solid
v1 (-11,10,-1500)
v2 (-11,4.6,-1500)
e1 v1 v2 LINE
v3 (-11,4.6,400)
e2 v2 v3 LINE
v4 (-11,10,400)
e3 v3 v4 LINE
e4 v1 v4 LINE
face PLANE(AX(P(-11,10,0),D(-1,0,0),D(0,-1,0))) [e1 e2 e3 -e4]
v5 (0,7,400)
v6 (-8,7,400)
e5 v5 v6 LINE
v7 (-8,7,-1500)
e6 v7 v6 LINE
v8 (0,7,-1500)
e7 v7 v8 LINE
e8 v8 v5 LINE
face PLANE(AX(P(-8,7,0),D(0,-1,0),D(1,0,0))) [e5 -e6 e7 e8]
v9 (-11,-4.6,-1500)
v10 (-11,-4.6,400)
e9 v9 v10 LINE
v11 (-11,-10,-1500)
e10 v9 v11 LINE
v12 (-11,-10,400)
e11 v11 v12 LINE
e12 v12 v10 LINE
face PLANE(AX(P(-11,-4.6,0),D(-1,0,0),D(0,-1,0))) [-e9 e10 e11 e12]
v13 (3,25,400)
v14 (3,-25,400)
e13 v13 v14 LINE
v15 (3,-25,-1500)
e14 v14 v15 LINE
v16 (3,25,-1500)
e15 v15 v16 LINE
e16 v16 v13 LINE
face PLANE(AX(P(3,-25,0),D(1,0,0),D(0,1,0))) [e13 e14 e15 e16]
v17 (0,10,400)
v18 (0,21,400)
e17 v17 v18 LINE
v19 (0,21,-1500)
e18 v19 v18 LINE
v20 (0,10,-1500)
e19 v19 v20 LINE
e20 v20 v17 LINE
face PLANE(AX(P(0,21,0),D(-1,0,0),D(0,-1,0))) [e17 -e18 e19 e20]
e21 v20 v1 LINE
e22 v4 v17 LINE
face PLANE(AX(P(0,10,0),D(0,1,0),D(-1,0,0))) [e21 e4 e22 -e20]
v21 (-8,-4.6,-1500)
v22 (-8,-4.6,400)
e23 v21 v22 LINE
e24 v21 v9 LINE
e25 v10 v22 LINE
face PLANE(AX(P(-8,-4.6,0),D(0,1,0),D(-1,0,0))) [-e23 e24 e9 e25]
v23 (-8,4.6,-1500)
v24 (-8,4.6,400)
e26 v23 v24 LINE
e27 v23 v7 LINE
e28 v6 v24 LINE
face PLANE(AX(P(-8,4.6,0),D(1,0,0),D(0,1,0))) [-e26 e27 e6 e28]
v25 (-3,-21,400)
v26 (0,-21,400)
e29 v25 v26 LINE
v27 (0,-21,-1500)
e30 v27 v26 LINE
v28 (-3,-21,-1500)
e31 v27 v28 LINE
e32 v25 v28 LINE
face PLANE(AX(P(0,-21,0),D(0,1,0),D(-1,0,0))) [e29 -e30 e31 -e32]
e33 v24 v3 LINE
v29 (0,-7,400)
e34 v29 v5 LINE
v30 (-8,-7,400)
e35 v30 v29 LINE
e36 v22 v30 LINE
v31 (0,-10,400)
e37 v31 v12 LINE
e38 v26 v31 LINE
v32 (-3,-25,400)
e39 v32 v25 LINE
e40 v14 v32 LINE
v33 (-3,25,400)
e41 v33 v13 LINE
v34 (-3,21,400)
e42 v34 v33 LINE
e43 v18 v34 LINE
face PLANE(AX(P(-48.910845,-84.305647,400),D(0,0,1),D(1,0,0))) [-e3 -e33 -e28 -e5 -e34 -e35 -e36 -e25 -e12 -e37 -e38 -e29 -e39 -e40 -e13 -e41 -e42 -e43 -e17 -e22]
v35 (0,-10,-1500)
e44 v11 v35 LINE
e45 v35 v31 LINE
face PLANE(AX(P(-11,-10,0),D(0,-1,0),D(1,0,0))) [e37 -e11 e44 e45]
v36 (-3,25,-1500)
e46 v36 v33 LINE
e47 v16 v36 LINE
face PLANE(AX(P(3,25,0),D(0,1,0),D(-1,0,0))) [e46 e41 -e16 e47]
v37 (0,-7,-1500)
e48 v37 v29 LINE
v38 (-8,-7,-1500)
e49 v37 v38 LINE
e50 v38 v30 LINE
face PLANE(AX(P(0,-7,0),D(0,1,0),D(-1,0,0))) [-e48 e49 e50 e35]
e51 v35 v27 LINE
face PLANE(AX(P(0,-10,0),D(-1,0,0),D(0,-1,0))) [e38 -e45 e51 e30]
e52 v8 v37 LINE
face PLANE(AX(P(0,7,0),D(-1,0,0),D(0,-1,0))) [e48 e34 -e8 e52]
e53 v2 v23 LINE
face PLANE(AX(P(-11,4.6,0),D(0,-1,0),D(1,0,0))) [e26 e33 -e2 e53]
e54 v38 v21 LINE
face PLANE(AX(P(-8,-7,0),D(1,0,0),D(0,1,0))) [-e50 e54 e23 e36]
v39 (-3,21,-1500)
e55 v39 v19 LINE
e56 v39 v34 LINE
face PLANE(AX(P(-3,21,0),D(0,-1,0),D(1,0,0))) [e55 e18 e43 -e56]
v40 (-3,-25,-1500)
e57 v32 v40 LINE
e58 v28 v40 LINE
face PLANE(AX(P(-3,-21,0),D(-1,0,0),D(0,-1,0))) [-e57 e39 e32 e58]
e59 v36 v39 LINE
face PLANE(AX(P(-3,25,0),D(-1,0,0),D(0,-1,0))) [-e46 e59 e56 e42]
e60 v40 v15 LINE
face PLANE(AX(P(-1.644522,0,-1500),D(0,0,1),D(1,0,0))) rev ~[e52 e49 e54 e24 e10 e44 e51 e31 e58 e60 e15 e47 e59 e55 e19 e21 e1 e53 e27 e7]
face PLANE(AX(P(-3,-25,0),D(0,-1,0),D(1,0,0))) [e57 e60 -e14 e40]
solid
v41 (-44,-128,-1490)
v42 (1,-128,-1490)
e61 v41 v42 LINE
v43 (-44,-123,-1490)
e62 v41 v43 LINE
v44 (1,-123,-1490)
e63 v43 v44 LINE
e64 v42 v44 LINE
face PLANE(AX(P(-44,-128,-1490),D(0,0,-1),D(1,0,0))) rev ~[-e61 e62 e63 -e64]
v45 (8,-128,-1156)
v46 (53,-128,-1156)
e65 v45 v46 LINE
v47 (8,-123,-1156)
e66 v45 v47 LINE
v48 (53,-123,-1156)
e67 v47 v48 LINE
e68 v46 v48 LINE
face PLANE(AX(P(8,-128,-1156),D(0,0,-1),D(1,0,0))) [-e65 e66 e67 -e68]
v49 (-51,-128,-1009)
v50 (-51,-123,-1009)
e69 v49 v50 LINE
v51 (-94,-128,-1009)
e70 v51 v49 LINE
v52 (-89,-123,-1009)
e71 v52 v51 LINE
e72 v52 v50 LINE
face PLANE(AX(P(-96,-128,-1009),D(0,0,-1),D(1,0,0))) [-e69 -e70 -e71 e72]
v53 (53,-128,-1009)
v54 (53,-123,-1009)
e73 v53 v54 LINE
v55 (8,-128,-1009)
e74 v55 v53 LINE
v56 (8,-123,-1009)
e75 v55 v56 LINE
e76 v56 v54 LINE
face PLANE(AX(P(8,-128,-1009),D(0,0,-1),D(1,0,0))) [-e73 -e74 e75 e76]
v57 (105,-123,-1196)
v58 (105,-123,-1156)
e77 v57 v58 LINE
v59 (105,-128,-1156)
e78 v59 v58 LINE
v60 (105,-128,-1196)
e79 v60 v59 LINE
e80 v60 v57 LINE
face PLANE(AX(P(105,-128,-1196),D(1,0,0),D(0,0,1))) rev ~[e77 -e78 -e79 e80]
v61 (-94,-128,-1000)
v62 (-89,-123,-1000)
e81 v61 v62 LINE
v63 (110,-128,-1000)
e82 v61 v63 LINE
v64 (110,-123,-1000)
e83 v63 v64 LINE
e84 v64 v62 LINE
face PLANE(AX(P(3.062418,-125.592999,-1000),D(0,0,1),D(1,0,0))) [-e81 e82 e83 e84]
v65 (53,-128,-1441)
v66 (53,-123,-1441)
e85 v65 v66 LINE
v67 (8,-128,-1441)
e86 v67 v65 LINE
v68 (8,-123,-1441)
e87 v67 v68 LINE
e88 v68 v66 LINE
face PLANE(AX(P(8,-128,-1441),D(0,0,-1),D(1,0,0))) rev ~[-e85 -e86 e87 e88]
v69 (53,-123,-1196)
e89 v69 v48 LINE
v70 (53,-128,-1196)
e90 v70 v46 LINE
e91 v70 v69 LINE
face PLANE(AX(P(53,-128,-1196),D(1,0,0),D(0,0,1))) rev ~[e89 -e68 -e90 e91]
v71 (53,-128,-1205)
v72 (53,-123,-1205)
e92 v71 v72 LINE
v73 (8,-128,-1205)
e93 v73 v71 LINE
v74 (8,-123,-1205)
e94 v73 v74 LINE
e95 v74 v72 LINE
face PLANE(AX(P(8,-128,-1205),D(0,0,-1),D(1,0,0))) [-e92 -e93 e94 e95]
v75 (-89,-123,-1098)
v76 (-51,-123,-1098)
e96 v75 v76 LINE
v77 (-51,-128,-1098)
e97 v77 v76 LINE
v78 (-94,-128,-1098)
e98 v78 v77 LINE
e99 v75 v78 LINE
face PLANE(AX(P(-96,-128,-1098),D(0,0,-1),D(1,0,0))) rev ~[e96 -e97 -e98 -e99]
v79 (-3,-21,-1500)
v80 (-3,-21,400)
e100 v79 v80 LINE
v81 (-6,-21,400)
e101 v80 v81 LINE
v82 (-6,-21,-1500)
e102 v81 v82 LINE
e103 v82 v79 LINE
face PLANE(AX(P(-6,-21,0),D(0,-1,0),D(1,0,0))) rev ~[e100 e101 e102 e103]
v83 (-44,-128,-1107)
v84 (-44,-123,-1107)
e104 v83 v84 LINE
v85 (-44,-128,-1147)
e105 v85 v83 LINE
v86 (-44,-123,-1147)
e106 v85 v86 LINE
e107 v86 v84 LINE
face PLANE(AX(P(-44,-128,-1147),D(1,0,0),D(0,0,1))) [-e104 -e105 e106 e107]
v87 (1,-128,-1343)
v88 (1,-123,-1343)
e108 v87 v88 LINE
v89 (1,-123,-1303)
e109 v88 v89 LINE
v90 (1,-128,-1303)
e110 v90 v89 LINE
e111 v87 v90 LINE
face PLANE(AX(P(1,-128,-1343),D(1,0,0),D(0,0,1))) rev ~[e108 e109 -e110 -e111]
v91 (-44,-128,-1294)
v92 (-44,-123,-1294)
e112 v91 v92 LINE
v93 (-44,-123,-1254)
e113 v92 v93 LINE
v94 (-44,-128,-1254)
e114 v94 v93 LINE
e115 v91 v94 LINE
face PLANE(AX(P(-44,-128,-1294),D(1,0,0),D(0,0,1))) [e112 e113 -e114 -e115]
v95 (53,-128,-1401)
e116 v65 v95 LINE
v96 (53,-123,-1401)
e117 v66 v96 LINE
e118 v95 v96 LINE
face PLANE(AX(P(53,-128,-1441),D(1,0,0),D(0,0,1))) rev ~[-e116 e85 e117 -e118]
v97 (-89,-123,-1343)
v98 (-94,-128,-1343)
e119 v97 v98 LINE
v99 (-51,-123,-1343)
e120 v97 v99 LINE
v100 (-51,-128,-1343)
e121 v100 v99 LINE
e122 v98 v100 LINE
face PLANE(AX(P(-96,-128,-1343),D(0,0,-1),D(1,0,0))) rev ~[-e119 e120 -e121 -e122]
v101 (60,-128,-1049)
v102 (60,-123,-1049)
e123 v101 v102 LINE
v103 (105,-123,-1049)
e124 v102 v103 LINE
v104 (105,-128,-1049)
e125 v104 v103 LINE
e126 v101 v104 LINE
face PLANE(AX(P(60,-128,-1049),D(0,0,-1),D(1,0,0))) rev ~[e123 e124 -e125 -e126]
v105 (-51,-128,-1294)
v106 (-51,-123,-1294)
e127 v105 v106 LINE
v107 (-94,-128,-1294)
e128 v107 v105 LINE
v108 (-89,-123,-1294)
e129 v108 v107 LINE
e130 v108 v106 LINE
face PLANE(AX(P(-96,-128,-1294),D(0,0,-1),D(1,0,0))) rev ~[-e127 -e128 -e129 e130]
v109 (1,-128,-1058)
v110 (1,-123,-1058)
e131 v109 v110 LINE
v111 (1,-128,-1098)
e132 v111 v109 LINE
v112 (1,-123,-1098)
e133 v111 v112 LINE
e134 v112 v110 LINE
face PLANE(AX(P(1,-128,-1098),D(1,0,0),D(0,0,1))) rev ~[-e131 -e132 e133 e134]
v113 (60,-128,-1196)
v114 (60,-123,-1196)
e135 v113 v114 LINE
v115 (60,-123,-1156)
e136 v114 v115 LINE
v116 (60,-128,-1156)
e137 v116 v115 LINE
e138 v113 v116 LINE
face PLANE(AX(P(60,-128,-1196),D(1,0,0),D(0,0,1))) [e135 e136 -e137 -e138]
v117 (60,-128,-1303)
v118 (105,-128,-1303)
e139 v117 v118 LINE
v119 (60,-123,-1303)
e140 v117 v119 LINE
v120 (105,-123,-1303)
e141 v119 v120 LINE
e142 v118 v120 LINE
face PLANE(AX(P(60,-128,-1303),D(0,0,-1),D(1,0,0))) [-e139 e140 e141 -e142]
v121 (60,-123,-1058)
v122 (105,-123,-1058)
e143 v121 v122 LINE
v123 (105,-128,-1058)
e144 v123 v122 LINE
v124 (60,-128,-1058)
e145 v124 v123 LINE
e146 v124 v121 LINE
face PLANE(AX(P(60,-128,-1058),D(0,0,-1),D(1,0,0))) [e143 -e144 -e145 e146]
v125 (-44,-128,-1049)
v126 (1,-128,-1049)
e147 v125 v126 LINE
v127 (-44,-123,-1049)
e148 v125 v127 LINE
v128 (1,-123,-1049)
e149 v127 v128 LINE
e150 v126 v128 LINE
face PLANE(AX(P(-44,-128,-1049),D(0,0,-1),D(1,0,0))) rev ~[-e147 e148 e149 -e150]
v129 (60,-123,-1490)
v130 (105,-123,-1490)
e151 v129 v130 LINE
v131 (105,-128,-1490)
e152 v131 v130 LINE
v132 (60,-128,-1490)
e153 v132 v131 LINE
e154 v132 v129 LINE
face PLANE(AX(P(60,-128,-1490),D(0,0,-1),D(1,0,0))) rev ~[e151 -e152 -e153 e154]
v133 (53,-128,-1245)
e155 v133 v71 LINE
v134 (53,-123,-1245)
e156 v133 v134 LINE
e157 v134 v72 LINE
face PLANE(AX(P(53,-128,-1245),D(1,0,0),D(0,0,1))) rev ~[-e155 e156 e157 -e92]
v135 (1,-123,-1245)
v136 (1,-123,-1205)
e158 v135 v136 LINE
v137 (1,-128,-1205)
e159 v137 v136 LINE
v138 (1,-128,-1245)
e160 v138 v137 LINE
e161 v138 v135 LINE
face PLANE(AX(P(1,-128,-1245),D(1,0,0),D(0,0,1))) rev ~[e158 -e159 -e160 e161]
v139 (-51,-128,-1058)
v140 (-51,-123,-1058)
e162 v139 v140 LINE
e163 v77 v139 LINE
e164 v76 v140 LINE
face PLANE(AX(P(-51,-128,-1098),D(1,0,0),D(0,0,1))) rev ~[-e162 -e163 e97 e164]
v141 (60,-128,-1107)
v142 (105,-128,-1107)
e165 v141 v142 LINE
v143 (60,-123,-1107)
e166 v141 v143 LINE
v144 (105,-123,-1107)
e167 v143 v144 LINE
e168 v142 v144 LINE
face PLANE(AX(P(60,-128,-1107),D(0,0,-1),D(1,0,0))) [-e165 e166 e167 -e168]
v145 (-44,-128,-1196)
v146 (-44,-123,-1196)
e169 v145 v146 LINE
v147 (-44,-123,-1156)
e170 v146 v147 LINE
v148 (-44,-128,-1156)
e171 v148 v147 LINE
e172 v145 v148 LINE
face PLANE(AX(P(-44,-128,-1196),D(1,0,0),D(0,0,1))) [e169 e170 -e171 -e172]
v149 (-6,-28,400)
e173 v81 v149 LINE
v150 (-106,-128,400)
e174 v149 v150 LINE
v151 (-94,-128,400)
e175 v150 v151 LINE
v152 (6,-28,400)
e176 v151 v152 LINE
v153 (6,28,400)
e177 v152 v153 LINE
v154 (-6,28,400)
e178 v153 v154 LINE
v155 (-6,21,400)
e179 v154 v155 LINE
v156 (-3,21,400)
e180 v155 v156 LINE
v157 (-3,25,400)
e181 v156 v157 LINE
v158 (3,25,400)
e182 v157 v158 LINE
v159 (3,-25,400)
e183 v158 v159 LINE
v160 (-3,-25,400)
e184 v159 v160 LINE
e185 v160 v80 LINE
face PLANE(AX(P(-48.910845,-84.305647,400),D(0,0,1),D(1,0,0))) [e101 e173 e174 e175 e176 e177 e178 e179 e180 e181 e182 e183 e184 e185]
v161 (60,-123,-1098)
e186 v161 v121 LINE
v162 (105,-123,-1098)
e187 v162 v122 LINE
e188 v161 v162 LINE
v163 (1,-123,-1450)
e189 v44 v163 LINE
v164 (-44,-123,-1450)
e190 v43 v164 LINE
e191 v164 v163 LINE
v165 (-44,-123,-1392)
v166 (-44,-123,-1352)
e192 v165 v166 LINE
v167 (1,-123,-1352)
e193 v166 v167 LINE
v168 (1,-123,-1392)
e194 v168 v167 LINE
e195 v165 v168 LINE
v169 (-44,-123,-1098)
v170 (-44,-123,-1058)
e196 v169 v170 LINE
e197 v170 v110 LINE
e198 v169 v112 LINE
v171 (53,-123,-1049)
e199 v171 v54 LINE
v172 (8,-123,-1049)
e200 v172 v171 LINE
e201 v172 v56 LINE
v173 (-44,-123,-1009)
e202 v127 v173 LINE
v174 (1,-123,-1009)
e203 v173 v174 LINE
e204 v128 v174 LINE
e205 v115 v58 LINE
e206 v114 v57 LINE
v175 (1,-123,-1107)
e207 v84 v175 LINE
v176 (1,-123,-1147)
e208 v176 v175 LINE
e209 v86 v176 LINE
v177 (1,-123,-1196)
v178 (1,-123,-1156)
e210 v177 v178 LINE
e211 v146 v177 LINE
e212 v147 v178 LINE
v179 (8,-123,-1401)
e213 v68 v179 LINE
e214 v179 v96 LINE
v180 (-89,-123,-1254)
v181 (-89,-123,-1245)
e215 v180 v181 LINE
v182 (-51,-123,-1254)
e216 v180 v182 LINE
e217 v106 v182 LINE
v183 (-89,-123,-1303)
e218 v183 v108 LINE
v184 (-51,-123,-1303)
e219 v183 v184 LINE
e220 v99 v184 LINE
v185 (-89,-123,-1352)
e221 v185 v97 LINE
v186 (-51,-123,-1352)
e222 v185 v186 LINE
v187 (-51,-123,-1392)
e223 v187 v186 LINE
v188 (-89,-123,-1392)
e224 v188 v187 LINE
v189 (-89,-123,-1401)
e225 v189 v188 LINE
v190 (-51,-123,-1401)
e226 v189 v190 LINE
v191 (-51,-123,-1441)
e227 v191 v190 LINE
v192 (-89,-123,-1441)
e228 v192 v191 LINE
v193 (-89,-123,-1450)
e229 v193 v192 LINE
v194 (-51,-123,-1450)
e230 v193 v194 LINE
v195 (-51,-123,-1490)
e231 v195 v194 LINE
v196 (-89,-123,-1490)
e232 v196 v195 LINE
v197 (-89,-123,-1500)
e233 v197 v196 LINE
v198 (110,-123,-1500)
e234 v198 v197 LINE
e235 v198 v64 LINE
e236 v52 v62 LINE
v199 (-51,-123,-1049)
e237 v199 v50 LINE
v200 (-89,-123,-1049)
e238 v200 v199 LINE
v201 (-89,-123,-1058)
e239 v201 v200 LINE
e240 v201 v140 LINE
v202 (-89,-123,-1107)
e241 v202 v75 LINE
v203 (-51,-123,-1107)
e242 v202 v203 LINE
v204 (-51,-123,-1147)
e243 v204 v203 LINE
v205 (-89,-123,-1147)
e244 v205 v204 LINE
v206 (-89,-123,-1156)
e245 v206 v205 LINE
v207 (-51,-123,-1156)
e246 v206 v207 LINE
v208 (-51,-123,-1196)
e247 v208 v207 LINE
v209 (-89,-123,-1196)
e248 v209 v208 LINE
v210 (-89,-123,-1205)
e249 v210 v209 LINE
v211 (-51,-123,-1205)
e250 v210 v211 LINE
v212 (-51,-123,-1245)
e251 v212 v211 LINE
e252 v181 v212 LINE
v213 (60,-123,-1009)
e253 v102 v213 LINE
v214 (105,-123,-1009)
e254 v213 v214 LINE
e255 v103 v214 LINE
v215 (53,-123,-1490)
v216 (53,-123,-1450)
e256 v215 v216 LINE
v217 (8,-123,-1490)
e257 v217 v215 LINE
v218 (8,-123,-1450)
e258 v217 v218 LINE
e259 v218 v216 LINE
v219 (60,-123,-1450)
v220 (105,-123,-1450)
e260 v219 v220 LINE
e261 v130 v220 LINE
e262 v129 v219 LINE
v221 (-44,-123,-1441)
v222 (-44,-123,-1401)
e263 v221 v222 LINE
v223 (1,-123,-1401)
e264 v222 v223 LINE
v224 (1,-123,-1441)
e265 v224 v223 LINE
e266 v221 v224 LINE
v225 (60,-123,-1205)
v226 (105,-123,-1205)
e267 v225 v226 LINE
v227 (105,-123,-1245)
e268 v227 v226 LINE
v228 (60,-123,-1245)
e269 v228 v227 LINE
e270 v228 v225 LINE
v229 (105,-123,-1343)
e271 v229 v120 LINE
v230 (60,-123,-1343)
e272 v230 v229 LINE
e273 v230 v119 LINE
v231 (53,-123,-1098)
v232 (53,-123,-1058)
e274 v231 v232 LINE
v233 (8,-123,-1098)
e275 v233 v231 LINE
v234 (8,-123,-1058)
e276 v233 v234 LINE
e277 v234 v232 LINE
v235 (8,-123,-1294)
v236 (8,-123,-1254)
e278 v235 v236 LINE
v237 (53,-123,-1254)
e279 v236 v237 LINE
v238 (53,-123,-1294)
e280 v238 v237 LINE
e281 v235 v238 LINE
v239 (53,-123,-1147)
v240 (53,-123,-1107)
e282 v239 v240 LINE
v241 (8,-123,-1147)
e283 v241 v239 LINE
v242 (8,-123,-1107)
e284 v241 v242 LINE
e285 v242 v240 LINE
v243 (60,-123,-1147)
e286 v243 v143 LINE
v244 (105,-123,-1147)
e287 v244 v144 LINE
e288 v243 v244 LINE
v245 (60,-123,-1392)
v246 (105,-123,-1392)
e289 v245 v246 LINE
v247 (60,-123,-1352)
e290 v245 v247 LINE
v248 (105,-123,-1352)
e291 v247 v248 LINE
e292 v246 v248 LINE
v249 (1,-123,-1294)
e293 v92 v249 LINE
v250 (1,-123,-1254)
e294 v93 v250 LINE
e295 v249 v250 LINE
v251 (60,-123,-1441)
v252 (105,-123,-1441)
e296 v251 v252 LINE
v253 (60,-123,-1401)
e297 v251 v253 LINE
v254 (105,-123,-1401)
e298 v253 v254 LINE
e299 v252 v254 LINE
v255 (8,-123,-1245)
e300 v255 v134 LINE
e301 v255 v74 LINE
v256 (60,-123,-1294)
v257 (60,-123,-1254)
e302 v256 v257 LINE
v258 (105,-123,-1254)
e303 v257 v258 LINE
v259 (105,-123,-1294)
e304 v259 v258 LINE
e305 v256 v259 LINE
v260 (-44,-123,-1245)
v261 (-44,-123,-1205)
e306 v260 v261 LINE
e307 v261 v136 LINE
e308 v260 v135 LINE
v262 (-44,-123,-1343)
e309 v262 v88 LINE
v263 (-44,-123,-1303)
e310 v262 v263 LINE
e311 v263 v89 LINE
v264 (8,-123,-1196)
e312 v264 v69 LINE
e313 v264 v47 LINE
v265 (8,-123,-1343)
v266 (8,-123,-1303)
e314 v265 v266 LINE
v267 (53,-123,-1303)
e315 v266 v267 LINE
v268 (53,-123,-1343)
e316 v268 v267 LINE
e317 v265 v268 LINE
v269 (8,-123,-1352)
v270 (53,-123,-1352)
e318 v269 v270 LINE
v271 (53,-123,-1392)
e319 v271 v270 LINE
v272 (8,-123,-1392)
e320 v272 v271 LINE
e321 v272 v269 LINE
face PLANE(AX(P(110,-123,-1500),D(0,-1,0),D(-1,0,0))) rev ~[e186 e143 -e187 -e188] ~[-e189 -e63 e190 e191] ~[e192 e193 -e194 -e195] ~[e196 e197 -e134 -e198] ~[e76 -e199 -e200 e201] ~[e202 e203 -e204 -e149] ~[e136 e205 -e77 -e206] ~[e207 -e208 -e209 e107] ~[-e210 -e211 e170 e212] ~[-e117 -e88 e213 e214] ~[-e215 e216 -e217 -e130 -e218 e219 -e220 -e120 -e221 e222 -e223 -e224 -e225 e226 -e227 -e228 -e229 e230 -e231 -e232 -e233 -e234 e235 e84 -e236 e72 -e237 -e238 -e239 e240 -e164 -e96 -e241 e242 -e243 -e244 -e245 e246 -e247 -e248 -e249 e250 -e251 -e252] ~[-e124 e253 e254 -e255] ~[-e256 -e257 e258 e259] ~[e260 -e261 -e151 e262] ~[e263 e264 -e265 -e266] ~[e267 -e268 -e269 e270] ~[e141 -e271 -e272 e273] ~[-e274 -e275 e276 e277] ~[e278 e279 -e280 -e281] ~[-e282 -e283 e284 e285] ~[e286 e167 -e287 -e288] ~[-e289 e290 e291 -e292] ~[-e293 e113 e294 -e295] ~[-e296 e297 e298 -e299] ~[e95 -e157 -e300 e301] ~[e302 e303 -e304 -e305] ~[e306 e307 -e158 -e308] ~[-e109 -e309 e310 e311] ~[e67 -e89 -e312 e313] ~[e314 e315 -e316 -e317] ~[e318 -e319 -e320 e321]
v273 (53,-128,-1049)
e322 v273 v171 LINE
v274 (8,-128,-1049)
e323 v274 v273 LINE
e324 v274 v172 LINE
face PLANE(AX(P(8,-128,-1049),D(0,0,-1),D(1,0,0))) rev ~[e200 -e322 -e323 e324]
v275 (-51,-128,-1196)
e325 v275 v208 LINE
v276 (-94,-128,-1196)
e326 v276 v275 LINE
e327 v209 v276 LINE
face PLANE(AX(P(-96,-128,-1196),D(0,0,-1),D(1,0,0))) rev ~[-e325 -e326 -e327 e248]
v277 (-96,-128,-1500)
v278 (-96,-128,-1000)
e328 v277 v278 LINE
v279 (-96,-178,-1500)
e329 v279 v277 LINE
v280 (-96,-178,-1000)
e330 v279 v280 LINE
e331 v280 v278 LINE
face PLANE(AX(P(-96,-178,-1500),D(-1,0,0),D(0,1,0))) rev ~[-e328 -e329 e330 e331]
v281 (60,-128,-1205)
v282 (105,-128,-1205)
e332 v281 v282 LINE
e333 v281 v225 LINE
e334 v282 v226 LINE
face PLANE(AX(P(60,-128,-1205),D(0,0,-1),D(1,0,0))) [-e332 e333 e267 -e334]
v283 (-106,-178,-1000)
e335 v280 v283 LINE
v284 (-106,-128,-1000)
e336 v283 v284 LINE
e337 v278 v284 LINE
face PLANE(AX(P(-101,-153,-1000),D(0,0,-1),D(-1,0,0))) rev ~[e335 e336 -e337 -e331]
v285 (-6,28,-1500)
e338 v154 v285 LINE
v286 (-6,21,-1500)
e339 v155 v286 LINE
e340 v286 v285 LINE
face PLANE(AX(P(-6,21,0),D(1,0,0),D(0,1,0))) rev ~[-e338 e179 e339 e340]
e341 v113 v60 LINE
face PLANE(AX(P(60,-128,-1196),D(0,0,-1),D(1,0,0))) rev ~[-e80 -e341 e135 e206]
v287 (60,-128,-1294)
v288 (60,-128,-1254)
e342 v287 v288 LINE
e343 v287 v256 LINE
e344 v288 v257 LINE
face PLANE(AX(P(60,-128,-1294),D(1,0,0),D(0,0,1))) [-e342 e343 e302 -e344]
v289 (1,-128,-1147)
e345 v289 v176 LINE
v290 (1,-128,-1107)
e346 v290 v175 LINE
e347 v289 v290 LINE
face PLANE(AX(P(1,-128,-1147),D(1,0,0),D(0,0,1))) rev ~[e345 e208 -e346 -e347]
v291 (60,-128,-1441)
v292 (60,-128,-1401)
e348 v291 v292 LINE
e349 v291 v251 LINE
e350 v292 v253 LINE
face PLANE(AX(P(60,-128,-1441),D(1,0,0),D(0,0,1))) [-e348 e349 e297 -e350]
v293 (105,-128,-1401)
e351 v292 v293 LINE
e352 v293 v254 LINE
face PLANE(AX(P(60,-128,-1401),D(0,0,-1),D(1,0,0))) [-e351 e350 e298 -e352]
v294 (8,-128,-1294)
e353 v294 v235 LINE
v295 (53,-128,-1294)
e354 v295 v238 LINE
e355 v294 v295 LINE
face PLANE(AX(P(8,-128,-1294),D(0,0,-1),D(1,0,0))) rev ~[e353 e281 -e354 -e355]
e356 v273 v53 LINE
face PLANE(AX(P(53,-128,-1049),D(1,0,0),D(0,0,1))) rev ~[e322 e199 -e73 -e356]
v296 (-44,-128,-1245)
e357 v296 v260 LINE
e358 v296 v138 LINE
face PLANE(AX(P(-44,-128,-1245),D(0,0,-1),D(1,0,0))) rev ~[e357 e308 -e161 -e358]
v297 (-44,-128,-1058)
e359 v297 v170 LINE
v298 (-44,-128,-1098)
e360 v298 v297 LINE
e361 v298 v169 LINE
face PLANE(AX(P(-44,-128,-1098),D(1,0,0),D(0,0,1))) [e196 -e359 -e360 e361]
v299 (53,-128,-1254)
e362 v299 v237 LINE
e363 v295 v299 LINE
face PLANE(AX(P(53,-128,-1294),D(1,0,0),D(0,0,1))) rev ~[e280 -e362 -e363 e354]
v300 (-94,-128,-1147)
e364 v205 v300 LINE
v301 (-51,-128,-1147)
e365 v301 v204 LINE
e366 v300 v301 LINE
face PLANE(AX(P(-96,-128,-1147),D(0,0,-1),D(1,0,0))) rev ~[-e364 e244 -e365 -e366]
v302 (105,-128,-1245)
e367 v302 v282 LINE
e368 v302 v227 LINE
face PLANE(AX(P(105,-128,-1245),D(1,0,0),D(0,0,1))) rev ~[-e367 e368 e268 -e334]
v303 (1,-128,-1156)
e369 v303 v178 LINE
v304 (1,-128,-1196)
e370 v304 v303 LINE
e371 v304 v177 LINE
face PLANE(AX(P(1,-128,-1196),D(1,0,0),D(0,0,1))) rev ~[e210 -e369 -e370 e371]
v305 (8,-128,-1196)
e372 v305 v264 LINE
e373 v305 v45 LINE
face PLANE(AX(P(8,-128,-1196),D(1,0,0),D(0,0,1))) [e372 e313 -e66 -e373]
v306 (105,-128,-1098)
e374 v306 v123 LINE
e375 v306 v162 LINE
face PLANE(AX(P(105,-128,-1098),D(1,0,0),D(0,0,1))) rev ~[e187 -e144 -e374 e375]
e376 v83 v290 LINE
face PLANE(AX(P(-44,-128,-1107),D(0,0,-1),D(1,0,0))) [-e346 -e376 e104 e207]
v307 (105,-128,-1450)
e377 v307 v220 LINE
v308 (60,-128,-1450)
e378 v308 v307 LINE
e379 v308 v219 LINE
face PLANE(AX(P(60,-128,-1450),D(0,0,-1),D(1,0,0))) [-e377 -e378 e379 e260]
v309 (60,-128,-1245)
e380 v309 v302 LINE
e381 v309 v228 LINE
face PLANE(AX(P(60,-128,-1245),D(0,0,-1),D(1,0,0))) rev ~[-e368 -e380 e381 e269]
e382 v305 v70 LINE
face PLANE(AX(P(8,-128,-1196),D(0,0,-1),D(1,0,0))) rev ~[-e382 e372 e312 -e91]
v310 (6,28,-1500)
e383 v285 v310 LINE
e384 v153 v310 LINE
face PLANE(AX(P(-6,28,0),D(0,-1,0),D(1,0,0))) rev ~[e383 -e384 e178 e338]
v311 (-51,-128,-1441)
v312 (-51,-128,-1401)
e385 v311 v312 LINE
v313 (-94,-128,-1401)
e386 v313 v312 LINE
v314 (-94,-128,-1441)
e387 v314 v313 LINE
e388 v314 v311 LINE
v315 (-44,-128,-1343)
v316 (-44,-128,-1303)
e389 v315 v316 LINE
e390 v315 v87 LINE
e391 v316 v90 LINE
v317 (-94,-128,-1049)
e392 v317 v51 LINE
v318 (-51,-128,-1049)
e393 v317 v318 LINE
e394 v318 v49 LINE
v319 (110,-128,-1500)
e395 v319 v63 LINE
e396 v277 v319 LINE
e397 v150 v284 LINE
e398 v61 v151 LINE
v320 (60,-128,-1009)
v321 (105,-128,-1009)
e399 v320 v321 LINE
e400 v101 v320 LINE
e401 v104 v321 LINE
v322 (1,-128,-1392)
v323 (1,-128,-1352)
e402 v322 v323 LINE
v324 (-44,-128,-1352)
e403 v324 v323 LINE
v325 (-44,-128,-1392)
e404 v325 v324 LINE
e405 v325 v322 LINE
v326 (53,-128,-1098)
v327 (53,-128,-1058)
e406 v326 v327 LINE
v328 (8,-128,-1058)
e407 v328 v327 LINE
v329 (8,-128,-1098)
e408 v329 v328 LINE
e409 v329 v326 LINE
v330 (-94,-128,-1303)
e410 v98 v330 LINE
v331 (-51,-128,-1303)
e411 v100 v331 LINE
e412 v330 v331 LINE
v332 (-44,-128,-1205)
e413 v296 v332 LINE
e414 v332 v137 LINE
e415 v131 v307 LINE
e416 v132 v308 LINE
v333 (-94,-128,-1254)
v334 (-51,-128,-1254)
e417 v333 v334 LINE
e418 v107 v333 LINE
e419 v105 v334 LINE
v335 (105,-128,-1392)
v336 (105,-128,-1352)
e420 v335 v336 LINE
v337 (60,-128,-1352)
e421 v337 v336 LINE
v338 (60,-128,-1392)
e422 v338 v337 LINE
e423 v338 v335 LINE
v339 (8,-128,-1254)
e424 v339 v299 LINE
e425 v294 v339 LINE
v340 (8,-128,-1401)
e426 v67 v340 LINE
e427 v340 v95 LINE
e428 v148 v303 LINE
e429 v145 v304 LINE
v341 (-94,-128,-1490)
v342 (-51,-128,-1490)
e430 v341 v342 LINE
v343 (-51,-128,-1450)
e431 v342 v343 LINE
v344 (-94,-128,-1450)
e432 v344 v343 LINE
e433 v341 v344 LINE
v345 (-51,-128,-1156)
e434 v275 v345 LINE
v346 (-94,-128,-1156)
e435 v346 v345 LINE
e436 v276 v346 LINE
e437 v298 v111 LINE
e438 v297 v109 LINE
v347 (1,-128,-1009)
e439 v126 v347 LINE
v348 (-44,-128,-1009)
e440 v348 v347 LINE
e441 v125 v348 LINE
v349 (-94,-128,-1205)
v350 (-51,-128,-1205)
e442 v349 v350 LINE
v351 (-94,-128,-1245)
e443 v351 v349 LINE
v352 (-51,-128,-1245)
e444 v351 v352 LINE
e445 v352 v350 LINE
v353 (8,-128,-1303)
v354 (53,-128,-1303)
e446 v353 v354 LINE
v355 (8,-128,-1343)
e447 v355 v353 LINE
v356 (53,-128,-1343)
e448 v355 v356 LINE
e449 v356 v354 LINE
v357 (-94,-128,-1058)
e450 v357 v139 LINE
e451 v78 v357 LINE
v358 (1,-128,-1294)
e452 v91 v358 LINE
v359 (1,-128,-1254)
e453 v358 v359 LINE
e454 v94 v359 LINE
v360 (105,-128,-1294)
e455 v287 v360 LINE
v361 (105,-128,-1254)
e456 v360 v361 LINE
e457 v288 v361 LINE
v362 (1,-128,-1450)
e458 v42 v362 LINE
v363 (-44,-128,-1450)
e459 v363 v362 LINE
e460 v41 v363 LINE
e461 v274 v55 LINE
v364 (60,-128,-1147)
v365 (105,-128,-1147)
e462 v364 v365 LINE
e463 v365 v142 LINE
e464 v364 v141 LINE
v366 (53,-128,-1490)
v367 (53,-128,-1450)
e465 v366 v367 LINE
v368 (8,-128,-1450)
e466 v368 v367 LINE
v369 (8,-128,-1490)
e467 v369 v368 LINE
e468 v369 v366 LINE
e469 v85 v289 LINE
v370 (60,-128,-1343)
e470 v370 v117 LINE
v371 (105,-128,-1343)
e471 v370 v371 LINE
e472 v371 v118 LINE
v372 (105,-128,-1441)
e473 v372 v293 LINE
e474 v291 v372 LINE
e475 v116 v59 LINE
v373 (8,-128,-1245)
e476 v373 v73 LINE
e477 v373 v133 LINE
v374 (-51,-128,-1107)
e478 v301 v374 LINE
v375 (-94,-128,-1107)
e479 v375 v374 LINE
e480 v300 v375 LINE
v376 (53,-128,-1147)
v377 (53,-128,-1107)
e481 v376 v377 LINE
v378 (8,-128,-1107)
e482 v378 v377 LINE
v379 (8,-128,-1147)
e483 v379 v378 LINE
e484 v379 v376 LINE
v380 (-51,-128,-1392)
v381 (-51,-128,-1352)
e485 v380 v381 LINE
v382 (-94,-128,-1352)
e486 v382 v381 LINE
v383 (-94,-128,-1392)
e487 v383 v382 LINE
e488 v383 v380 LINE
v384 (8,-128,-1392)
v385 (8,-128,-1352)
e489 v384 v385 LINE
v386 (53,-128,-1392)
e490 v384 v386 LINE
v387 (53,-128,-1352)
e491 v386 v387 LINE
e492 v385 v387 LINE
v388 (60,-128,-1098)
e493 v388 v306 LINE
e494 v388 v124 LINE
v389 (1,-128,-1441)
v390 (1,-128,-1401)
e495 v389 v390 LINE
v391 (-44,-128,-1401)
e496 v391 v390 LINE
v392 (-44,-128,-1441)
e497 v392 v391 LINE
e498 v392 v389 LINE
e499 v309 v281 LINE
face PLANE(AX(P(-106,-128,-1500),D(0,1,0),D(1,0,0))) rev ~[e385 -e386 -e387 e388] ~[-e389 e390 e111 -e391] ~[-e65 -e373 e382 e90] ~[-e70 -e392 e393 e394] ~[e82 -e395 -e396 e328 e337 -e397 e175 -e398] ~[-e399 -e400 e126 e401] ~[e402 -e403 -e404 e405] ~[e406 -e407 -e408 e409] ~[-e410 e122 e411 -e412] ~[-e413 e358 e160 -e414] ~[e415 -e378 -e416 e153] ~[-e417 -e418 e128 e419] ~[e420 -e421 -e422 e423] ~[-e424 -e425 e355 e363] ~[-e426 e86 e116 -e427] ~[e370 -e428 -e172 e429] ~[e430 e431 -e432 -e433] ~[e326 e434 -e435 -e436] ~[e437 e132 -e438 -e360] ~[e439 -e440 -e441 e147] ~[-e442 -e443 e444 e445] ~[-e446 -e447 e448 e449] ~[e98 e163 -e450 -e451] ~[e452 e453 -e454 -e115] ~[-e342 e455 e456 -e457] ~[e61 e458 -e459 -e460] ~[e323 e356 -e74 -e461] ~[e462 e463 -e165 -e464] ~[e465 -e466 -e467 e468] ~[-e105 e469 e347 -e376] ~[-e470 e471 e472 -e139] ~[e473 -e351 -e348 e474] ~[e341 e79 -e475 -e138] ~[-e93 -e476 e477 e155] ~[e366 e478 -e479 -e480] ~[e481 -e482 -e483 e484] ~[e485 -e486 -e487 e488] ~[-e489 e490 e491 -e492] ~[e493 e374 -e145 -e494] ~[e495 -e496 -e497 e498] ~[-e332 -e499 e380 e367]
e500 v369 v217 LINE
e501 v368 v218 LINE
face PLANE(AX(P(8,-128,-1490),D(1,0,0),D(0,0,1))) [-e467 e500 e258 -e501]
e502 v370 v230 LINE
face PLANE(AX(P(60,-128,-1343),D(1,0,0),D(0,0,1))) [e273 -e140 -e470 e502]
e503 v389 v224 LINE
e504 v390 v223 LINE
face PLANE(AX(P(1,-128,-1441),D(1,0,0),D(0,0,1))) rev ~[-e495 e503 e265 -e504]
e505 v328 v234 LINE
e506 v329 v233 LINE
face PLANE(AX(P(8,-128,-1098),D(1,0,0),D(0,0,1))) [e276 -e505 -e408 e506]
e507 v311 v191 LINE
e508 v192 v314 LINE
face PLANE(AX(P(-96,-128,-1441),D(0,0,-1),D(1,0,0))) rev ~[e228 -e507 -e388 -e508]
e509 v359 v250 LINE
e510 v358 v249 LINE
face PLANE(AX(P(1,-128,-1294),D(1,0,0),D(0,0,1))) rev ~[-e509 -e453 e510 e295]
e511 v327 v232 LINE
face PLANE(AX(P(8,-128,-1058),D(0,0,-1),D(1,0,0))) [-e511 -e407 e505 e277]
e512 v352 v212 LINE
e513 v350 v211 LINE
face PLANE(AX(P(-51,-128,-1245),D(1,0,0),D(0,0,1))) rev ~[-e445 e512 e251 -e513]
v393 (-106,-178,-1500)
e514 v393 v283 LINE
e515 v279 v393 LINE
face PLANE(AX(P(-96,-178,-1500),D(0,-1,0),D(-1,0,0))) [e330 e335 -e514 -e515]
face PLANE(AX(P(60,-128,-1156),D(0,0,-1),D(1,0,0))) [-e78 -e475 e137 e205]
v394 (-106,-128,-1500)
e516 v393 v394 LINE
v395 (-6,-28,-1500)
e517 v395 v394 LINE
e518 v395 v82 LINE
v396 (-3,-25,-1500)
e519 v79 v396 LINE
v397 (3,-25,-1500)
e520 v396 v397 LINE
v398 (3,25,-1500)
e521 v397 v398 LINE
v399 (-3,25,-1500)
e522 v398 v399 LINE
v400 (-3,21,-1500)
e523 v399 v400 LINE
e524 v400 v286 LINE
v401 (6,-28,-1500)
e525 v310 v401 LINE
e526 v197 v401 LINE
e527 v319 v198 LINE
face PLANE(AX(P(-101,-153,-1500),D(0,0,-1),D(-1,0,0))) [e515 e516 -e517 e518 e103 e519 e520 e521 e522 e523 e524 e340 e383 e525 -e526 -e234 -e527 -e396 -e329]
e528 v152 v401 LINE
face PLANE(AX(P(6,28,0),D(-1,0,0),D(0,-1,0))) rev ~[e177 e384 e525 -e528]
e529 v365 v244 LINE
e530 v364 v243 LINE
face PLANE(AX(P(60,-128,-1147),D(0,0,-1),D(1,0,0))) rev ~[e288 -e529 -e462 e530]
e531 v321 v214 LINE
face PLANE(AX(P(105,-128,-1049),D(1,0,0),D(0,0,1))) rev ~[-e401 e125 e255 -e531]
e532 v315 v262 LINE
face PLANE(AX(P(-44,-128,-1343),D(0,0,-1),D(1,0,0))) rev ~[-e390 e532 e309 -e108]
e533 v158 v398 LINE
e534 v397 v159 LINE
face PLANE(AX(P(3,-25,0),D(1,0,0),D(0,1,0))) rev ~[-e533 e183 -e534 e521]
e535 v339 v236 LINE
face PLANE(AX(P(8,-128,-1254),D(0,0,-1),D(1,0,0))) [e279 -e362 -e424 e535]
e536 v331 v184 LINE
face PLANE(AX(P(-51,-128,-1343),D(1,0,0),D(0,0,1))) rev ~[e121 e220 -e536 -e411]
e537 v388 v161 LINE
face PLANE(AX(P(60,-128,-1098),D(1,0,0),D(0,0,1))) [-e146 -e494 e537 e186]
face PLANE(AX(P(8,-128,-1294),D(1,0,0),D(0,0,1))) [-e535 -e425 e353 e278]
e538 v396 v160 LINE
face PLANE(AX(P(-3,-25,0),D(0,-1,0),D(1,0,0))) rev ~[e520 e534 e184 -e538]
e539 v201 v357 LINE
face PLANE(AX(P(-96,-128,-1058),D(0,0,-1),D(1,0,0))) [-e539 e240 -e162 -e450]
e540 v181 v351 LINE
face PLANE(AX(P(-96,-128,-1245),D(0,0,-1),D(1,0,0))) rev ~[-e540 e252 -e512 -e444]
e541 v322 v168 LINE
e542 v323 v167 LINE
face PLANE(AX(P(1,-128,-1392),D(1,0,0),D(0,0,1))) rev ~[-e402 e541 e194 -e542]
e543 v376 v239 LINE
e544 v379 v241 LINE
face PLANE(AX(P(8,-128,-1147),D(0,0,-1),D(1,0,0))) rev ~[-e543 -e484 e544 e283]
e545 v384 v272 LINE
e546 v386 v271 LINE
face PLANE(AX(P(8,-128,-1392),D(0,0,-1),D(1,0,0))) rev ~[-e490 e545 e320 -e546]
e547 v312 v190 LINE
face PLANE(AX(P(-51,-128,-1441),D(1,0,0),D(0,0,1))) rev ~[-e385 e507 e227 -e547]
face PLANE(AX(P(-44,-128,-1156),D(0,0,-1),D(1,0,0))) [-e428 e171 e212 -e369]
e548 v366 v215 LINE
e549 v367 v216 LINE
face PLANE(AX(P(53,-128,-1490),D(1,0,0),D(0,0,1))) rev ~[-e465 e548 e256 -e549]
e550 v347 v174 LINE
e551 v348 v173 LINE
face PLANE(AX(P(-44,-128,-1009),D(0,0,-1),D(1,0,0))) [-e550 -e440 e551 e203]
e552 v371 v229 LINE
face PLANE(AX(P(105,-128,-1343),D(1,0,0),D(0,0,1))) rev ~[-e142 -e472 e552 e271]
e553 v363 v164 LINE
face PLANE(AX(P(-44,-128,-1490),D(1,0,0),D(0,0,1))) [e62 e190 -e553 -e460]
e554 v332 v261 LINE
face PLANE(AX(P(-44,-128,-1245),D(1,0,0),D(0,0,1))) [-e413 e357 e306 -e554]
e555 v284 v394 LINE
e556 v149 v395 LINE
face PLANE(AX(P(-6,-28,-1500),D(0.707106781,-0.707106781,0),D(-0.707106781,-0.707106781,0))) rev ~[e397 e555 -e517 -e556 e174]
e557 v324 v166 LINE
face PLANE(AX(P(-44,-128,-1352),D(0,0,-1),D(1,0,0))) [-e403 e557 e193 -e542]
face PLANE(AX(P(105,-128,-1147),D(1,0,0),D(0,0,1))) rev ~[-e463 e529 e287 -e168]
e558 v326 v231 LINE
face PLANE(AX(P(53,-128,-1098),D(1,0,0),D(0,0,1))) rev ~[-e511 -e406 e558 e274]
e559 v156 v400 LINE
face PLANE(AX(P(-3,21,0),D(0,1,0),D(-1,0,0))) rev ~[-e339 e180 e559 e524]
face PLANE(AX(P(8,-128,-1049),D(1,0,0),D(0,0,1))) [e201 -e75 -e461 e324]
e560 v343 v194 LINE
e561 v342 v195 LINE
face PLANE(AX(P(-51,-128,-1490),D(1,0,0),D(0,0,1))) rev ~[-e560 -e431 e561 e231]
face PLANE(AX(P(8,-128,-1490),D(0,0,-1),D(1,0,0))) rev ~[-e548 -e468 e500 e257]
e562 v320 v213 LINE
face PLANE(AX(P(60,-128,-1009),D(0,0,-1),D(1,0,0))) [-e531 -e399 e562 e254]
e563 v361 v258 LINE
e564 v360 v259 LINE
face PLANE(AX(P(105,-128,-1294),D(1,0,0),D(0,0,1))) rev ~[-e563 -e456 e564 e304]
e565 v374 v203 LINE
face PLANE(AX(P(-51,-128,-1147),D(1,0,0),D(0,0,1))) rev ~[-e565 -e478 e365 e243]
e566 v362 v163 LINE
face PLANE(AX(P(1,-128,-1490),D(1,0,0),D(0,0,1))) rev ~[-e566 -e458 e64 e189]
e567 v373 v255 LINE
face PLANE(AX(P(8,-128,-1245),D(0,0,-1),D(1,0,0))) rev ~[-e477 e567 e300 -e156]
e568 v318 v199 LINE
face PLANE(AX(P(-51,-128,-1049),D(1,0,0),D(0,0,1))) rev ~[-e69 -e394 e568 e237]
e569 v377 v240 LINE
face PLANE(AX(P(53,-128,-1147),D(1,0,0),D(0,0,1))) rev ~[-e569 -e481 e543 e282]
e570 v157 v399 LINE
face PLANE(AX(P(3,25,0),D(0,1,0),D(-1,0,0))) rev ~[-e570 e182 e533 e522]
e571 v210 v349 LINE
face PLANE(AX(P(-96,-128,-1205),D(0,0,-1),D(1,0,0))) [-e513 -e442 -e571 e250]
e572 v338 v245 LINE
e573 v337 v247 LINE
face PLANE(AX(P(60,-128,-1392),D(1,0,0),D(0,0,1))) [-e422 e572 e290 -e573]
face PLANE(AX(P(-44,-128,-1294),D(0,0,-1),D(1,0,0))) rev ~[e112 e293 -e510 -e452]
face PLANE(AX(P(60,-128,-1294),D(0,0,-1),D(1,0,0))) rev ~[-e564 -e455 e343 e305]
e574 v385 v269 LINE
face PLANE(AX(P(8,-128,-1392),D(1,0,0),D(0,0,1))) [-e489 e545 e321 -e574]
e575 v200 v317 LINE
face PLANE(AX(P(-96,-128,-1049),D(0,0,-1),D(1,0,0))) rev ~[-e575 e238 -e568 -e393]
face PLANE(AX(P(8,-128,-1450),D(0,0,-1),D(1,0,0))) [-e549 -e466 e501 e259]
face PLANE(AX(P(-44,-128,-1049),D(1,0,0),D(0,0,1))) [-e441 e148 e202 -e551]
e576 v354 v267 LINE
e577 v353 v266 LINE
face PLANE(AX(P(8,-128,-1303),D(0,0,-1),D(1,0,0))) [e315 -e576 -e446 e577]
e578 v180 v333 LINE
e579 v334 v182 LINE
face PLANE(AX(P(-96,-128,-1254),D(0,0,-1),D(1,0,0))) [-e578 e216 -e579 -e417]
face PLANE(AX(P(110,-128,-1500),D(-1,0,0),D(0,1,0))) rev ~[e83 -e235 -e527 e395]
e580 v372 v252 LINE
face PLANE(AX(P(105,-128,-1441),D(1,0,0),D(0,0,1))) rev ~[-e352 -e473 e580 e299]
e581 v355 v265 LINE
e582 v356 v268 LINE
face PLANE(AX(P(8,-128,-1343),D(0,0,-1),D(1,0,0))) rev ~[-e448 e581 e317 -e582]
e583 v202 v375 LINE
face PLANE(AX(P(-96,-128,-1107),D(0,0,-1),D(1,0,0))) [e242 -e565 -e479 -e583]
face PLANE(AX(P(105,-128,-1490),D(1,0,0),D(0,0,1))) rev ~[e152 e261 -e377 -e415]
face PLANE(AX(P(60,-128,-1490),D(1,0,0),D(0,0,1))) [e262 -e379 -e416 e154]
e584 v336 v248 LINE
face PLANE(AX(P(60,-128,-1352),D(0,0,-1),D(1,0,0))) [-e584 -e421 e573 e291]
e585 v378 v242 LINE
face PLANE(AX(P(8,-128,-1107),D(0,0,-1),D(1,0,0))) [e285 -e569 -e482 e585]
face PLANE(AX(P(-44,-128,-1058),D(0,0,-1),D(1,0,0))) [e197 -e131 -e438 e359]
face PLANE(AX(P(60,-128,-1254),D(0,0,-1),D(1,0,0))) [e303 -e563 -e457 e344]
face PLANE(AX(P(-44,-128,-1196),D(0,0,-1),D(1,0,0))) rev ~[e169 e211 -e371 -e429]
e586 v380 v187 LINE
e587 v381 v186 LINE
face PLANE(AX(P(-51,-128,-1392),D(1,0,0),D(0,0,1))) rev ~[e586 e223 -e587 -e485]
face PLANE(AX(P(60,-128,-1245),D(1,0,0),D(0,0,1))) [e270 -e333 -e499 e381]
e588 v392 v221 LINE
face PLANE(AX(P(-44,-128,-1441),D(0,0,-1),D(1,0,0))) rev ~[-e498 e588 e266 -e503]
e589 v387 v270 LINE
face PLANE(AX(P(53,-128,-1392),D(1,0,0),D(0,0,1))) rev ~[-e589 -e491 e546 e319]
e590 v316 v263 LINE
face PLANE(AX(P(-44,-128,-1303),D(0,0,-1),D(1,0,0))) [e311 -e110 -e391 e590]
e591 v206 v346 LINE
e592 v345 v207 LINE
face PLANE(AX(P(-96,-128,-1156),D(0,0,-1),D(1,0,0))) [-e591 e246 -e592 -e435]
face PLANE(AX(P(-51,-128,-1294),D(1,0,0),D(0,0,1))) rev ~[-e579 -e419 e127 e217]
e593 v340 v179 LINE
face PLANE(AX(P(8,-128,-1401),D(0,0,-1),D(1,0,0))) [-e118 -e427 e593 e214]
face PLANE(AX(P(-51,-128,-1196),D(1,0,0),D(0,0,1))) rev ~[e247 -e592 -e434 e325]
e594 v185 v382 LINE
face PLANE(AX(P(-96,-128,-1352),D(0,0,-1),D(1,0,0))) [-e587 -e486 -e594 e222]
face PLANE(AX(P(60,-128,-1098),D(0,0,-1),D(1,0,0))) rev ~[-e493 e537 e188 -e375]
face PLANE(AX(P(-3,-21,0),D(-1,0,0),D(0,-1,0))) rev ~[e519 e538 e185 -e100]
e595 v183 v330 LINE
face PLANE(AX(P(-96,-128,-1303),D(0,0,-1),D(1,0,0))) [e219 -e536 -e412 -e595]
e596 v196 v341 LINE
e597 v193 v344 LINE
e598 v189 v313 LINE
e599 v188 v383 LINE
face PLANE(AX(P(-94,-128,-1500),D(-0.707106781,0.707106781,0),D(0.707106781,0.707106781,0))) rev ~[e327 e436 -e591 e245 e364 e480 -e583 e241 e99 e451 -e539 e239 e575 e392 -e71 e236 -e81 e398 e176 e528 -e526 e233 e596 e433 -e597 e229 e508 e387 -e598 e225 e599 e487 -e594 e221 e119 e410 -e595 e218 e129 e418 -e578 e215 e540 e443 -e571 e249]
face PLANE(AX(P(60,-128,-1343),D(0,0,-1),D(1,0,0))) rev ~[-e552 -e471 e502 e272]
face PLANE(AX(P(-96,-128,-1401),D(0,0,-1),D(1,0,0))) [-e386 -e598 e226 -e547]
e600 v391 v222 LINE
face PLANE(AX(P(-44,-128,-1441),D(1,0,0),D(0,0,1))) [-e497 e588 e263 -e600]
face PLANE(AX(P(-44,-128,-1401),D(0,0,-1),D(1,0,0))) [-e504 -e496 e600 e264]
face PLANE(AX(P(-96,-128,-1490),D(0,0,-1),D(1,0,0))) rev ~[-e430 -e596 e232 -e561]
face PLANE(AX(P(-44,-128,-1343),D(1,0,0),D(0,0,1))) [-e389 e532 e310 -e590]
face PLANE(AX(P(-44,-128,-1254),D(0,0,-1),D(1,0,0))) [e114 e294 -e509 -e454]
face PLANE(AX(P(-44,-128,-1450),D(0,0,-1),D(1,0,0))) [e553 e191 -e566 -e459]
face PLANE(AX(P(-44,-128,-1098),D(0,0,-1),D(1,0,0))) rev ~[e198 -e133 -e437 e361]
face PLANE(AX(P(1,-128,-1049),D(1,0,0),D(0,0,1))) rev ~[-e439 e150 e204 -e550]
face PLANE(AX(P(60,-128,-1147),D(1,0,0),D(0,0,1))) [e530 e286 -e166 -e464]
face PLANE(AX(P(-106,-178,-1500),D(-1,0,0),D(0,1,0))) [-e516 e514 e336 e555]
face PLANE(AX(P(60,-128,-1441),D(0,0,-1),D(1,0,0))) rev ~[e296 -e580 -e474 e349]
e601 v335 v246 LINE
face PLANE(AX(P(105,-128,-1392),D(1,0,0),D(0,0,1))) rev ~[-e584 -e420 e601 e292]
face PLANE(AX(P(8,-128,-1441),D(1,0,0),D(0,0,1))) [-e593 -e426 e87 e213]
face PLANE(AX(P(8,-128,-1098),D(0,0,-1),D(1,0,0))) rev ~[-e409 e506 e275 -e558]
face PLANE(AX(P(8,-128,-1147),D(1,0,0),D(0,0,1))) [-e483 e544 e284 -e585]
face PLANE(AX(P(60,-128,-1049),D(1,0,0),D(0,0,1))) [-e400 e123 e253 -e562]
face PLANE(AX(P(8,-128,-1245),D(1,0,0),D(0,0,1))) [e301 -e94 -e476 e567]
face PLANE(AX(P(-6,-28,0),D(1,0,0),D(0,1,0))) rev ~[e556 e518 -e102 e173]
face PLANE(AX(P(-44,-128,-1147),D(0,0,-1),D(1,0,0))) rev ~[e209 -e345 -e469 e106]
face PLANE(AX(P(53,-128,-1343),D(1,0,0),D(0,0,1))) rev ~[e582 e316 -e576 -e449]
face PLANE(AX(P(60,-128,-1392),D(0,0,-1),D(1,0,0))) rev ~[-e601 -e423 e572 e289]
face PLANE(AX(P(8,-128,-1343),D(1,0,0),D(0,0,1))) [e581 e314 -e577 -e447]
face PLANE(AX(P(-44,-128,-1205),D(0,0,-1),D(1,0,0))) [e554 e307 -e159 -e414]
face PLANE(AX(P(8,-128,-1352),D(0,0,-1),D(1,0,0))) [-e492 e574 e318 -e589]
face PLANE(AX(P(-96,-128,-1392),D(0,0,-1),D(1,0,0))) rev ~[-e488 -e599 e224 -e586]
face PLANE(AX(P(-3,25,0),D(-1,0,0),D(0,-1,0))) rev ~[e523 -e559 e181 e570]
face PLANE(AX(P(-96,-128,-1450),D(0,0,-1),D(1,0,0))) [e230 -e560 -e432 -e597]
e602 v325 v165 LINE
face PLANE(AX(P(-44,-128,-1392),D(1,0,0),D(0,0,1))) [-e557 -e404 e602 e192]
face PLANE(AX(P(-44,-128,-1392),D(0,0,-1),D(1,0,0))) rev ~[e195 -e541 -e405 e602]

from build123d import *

# Parameters (mm, degrees)
EXTRUDE_1_DEPTH        = 1500
EXTRUDE_2_DEPTH        = 1500
EXTRUDE_3_DEPTH        = 3000
EXTRUDE_4_DEPTH        = 500
SKETCH_5_W             = 10
SKETCH_5_H             = 50
EXTRUDE_5_DEPTH        = 500
CUT_EXTRUDE_1_REACH    = 1514.097
SKETCH_6_W             = 45
SKETCH_6_H             = 40
PATTERN_LINEAR_1_COUNT = 10
PATTERN_LINEAR_1_PITCH = 49
SKETCH_7_W             = 228.888066114
SKETCH_7_H             = 283.388705447
CUT_EXTRUDE_2_DEPTH    = 1100


with BuildPart() as part:
    # 草图1 → 凸台-拉伸1 (new, symmetric)
    with BuildSketch(Plane.XY):
        Polygon((3, -25), (3, 25), (-3, 25), (-3, 21), (0, 21), (0, 10), (-11, 10), (-11, 4.6), (-8, 4.6), (-8, 7), (0, 7), (0, -7), (-8, -7), (-8, -4.6), (-11, -4.6), (-11, -10), (0, -10), (0, -21), (-3, -21), (-3, -25), align=None)
    extrude(amount=EXTRUDE_1_DEPTH, both=True)


with BuildPart() as body_2:
    # 草图2 → 凸台-拉伸2 (new, symmetric)
    with BuildSketch(Plane.XY):
        Polygon((3, -25), (3, 25), (-3, 25), (-3, 21), (-6, 21), (-6, 28), (6, 28), (6, -28), (-6, -28), (-6, -21), (-3, -21), (-3, -25), align=None)
    extrude(amount=EXTRUDE_2_DEPTH, both=True)

    # 草图3 → 凸台-拉伸3 (add, through all)
    with BuildSketch(Plane(origin=(0, 0, -1500), x_dir=(-1, 0, 0), z_dir=(0, 0, -1))):
        Polygon((6, -28), (106, -128), (94, -128), (-6, -28), align=None)
    extrude(amount=-EXTRUDE_3_DEPTH)

    # 草图4 → 凸台-拉伸4 (add)
    with BuildSketch(Plane(origin=(0, 0, -1500), x_dir=(-1, 0, 0), z_dir=(0, 0, -1))):
        Polygon((106, -128), (-110, -128), (-110, -123), (89.715789032, -123), align=None)
    extrude(amount=-EXTRUDE_4_DEPTH)

    # 草图5 → 凸台-拉伸5 (add)
    with BuildSketch(Plane(origin=(0, 0, -1500), x_dir=(-1, 0, 0), z_dir=(0, 0, -1))):
        with Locations((101, -153)):
            Rectangle(SKETCH_5_W, SKETCH_5_H)
    extrude(amount=-EXTRUDE_5_DEPTH)

    # 切除-拉伸1: up to this face of the body (flat: up to its plane)
    cut_extrude_1_end = Plane(body_2.part.faces().sort_by_distance((-43.600840336, -77.600840336, 10.504201681))[0])
    # 草图6 → 切除-拉伸1 (cut, up to the picked face)
    with BuildSketch(Plane.XZ.offset(128), mode=Mode.PRIVATE) as cut_extrude_1_sk1:
        with Locations((-73.5, -1470)):
            Rectangle(SKETCH_6_W, SKETCH_6_H)
    cut_extrude_1_tool1 = split(extrude(cut_extrude_1_sk1.sketch, amount=-CUT_EXTRUDE_1_REACH, mode=Mode.PRIVATE), bisect_by=cut_extrude_1_end, keep=Keep.BOTH, mode=Mode.PRIVATE)
    # 草图6 → 切除-拉伸1 (cut, up to the picked face)
    with BuildSketch(Plane.XZ.offset(128), mode=Mode.PRIVATE) as cut_extrude_1_sk2:
        with Locations((-21.5, -1470)):
            Rectangle(SKETCH_6_W, SKETCH_6_H)
    cut_extrude_1_tool2 = split(extrude(cut_extrude_1_sk2.sketch, amount=-CUT_EXTRUDE_1_REACH, mode=Mode.PRIVATE), bisect_by=cut_extrude_1_end, keep=Keep.BOTH, mode=Mode.PRIVATE)
    # 草图6 → 切除-拉伸1 (cut, up to the picked face)
    with BuildSketch(Plane.XZ.offset(128), mode=Mode.PRIVATE) as cut_extrude_1_sk3:
        with Locations((30.5, -1470)):
            Rectangle(SKETCH_6_W, SKETCH_6_H)
    cut_extrude_1_tool3 = split(extrude(cut_extrude_1_sk3.sketch, amount=-CUT_EXTRUDE_1_REACH, mode=Mode.PRIVATE), bisect_by=cut_extrude_1_end, keep=Keep.BOTH, mode=Mode.PRIVATE)
    # 草图6 → 切除-拉伸1 (cut, up to the picked face)
    with BuildSketch(Plane.XZ.offset(128), mode=Mode.PRIVATE) as cut_extrude_1_sk4:
        with Locations((82.5, -1470)):
            Rectangle(SKETCH_6_W, SKETCH_6_H)
    cut_extrude_1_tool4 = split(extrude(cut_extrude_1_sk4.sketch, amount=-CUT_EXTRUDE_1_REACH, mode=Mode.PRIVATE), bisect_by=cut_extrude_1_end, keep=Keep.BOTH, mode=Mode.PRIVATE)
    cut_extrude_1_1 = cut_extrude_1_tool1.solids().sort_by(Axis((-73.5, -128, -1470), (0, 1, 0)))[0]
    add(cut_extrude_1_1, mode=Mode.SUBTRACT)
    cut_extrude_1_2 = cut_extrude_1_tool2.solids().sort_by(Axis((-21.5, -128, -1470), (0, 1, 0)))[0]
    add(cut_extrude_1_2, mode=Mode.SUBTRACT)
    cut_extrude_1_3 = cut_extrude_1_tool3.solids().sort_by(Axis((30.5, -128, -1470), (0, 1, 0)))[0]
    add(cut_extrude_1_3, mode=Mode.SUBTRACT)
    cut_extrude_1_4 = cut_extrude_1_tool4.solids().sort_by(Axis((82.5, -128, -1470), (0, 1, 0)))[0]
    add(cut_extrude_1_4, mode=Mode.SUBTRACT)
    cut_extrude_1 = cut_extrude_1_1 + cut_extrude_1_2 + cut_extrude_1_3 + cut_extrude_1_4  # 切除-拉伸1 as one shape, for the pattern or mirror that repeats it

    # 阵列(线性)1: 切除-拉伸1 ×10
    with Locations(*[(0, 0, i * PATTERN_LINEAR_1_PITCH) for i in range(1, PATTERN_LINEAR_1_COUNT)]):
        add(cut_extrude_1, mode=Mode.SUBTRACT)


with BuildPart() as cut_extrude_2_tool:
    # 草图7 → 切除-拉伸2 (new body)
    with BuildSketch(Plane.XY.offset(1500)):
        with Locations((-48.91084533, -84.305647276)):
            Rectangle(SKETCH_7_W, SKETCH_7_H)
    extrude(amount=-CUT_EXTRUDE_2_DEPTH)


with BuildPart() as part_1:
    add(part.part)

    # 切除-拉伸2: cut by cut_extrude_2_tool
    add(cut_extrude_2_tool.part, mode=Mode.SUBTRACT)


with BuildPart() as body_2_1:
    add(body_2.part)

    # 切除-拉伸2: cut by cut_extrude_2_tool
    add(cut_extrude_2_tool.part, mode=Mode.SUBTRACT)


solid = Compound([part_1.part, body_2_1.part])
